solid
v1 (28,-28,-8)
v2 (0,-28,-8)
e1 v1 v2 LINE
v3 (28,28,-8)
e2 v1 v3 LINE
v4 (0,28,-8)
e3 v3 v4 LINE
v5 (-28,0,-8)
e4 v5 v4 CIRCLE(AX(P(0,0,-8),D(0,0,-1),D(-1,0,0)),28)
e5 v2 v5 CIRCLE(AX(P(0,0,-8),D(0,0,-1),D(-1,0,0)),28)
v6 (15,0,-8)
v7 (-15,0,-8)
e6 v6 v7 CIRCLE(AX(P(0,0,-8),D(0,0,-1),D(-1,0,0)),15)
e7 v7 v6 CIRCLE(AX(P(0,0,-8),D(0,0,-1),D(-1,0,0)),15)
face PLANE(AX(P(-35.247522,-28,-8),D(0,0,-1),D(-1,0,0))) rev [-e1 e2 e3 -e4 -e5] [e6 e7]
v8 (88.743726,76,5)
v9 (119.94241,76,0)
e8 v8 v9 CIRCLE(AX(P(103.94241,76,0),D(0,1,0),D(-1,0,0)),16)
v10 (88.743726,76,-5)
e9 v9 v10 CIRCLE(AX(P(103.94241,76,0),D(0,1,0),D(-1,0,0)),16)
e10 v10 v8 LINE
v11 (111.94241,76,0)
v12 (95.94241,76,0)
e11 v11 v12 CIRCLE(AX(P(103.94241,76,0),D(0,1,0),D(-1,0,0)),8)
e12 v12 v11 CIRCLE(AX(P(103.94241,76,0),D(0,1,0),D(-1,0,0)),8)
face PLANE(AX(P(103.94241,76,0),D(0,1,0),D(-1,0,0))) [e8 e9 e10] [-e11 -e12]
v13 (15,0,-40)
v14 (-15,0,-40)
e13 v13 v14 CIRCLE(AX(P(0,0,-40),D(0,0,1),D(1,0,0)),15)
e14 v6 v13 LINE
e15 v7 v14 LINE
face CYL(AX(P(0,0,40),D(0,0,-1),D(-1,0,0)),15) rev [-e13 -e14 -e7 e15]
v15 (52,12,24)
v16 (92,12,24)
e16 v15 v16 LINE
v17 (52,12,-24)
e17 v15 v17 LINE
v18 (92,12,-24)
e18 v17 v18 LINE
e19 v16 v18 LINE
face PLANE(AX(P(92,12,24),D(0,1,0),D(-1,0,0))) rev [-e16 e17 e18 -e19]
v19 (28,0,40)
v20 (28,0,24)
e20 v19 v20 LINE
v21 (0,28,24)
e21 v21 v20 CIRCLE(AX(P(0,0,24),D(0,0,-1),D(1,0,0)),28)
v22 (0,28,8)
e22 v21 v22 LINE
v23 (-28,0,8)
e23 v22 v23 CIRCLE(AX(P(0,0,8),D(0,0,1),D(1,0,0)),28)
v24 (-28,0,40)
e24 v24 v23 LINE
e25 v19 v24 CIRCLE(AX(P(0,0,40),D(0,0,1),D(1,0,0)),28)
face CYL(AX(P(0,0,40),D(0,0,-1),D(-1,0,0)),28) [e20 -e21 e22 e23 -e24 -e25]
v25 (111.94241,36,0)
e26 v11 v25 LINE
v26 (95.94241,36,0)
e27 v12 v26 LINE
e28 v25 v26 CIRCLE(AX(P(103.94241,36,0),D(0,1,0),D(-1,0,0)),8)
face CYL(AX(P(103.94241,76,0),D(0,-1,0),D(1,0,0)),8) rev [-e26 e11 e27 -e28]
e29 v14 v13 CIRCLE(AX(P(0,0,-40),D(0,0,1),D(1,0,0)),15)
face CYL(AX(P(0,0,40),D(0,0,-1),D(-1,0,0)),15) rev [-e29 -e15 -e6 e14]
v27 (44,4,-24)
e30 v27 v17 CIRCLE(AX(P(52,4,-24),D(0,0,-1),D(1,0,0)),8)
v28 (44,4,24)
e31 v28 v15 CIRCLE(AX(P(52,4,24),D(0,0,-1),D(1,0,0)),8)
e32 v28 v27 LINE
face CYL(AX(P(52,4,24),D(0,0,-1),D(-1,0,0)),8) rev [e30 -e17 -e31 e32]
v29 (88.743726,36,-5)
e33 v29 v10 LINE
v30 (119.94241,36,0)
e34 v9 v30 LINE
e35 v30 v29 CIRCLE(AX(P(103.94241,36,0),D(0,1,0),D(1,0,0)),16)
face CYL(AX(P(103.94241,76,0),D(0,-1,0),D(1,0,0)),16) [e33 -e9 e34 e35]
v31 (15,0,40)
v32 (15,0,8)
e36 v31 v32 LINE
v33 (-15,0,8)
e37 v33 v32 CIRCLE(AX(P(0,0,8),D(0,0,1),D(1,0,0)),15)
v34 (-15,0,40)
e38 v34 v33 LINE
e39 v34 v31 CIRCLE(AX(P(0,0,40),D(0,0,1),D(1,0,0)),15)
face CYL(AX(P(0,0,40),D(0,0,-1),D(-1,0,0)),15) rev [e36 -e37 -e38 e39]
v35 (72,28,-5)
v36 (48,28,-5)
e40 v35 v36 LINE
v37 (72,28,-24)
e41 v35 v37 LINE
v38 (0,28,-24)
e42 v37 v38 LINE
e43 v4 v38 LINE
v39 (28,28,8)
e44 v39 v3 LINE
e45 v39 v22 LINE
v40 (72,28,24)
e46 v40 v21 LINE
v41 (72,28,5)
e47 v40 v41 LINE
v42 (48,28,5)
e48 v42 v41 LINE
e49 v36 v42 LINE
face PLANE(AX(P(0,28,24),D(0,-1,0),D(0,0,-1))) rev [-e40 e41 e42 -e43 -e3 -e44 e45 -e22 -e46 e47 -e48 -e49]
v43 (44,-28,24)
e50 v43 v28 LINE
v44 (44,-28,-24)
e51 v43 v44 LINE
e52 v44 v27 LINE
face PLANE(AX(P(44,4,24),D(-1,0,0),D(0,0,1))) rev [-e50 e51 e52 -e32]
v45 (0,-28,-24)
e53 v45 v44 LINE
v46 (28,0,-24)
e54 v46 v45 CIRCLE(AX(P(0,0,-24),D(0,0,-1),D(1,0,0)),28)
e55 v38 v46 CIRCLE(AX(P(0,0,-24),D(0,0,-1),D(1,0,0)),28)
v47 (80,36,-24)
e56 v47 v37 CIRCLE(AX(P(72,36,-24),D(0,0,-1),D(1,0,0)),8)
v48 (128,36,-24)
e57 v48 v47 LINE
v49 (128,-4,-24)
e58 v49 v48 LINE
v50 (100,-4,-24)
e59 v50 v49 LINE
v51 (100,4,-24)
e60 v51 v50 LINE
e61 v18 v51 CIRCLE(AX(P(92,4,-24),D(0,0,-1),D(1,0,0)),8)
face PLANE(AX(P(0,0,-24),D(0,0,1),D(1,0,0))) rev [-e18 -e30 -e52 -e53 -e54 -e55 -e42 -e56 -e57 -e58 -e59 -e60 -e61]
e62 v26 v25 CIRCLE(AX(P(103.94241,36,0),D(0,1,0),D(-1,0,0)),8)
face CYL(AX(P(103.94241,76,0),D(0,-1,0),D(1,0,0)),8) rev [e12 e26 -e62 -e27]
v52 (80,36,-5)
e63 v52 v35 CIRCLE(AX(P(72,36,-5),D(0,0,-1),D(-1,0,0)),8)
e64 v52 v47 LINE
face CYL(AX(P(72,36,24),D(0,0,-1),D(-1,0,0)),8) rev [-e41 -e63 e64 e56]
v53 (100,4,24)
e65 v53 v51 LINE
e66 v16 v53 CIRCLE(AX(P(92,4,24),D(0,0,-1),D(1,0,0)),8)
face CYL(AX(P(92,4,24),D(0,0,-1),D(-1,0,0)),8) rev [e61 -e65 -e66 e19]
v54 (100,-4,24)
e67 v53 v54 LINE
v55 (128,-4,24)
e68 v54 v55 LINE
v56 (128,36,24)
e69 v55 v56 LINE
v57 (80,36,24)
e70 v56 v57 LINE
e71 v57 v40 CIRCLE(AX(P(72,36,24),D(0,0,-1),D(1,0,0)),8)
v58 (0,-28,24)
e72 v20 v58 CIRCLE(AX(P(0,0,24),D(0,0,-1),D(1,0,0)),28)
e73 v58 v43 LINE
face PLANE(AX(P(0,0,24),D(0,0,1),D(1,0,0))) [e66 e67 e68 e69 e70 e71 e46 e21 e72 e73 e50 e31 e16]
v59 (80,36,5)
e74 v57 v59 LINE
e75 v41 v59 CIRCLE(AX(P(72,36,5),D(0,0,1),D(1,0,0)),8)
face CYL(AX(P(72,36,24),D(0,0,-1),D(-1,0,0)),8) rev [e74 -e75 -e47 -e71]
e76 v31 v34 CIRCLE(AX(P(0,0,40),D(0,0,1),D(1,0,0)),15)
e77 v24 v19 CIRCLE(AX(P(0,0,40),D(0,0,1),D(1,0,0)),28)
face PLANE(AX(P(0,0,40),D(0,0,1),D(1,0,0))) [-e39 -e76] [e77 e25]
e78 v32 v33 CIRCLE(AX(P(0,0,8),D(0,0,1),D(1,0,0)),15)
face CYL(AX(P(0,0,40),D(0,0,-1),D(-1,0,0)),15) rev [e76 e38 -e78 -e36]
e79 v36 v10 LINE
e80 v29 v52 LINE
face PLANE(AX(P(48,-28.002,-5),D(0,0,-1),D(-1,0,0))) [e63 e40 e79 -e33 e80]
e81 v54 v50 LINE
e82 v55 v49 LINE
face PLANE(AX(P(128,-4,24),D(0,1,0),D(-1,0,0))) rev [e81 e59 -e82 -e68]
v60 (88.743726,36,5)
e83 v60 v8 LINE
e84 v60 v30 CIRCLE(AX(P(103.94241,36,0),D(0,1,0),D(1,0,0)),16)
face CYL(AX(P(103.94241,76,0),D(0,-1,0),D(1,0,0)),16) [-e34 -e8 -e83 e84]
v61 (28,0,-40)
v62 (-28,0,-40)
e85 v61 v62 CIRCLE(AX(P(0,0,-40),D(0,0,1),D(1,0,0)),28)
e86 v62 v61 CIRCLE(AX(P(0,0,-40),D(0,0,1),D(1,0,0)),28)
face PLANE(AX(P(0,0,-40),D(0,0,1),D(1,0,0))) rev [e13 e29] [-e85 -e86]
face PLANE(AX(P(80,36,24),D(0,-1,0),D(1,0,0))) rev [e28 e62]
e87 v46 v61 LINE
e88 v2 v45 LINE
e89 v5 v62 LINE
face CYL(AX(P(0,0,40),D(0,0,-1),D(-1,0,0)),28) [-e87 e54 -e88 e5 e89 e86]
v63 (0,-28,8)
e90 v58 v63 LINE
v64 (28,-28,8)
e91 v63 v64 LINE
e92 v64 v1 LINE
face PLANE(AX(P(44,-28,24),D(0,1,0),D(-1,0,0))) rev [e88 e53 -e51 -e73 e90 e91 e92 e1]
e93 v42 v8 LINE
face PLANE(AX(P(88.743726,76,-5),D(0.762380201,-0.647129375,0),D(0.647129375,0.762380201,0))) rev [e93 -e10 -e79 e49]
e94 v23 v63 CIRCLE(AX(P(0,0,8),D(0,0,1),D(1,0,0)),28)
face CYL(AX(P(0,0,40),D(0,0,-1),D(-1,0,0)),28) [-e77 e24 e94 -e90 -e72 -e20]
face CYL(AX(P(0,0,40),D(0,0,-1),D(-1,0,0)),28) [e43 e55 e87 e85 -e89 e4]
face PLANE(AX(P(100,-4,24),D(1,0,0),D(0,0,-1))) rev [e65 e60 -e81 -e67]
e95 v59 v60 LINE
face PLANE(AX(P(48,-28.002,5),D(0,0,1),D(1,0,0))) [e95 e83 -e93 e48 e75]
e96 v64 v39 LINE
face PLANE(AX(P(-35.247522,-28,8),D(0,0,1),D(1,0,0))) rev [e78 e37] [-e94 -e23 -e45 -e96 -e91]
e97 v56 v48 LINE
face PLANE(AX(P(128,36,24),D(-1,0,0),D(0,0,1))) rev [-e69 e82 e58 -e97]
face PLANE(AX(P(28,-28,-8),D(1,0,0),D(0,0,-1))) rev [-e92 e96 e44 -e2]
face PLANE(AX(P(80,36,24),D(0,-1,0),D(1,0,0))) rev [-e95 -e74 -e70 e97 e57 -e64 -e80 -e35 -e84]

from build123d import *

# Parameters (mm, degrees)
PIVOT_HUB_SKETCH_R            = 28
PIVOT_HUB_SKETCH_R_2          = 15
PIVOT_HUB_56_BORE_30_DEPTH    = 40
LINK_ARM_DEPTH                = 24
FORK_SLOT_SKETCH_W            = 63.247521784
FORK_SLOT_SKETCH_H            = 16
FORK_SLOT_16_DEPTH            = 146.327216997
UPRIGHT_BOSS_SKETCH_R         = 16
UPRIGHT_BOSS_SKETCH_R_2       = 8
UPRIGHT_BOSS_32_BORE_16_DEPTH = 40
JUNCTION_PAD_REACH            = 171.706
TRIANGULAR_RELIEF_CUT_DEPTH   = 10


with BuildPart() as part:
    # Pivot Hub Sketch → Pivot Hub Ø56 Bore Ø30 (new, symmetric)
    with BuildSketch(Plane.XY):
        Circle(PIVOT_HUB_SKETCH_R)
        Circle(PIVOT_HUB_SKETCH_R_2, mode=Mode.SUBTRACT)
    extrude(amount=PIVOT_HUB_56_BORE_30_DEPTH, both=True)

    # Link Arm Profile → Link Arm (add, symmetric)
    with BuildSketch(Plane.XY):
        with BuildLine():
            Line((0, 28), (72, 28))
            ThreePointArc((72, 28), (77.656854249, 30.343145751), (80, 36))
            Line((80, 36), (128, 36))
            Line((128, 36), (128, -4))
            Line((128, -4), (100, -4))
            Line((100, -4), (100, 4))
            ThreePointArc((100, 4), (97.656854249, 9.656854249), (92, 12))
            Line((92, 12), (52, 12))
            ThreePointArc((52, 12), (46.343145751, 9.656854249), (44, 4))
            Line((44, 4), (44, -28))
            Line((44, -28), (0, -28))
            ThreePointArc((0, -28), (28, 0), (0, 28))
        make_face()
    extrude(amount=LINK_ARM_DEPTH, both=True)

    # Fork Slot Sketch → Fork Slot 16 (cut, through all)
    with BuildSketch(Plane(origin=(0, 28, 0), x_dir=(1, 0, 0), z_dir=(0, 1, 0))):
        with Locations((-3.623760892, 0)):
            Rectangle(FORK_SLOT_SKETCH_W, FORK_SLOT_SKETCH_H)
    extrude(amount=-FORK_SLOT_16_DEPTH, mode=Mode.SUBTRACT)

    # Upright Boss Sketch → Upright Boss Ø32 Bore Ø16 (add)
    with BuildSketch(Plane(origin=(0, 36, 0), x_dir=(1, 0, 0), z_dir=(0, 1, 0))):
        with Locations((103.942410132, 0)):
            Circle(UPRIGHT_BOSS_SKETCH_R)
        with Locations(Location((103.942410132, 0, 0), (0, 0, 180))):
            Circle(UPRIGHT_BOSS_SKETCH_R_2, mode=Mode.SUBTRACT)
    extrude(amount=UPRIGHT_BOSS_32_BORE_16_DEPTH)

    # Junction Pad Sketch → Junction Pad (add, up to next)
    with BuildSketch(Plane(origin=(0, 76, 0), x_dir=(1, 0, 0), z_dir=(0, 1, 0)), mode=Mode.PRIVATE) as junction_pad_sk1:
        with BuildLine():
            Line((48, 5), (88.743725978, 5))
            ThreePointArc((88.743725978, 5), (87.942410132, 0), (88.743725978, -5))
            Line((88.743725978, -5), (48, -5))
            Line((48, -5), (48, 5))
        make_face()
    junction_pad_tool1 = extrude(junction_pad_sk1.sketch, amount=-JUNCTION_PAD_REACH, mode=Mode.PRIVATE) - part.part
    add(junction_pad_tool1.solids().sort_by_distance((68.104095, 76, 0))[0])

    # Relief Cut Sketch → Triangular Relief Cut (cut)
    with BuildSketch(Plane.XY.offset(5)):
        Polygon((88.743725978, 76), (48, 28), (48, 76), align=None)
    extrude(amount=-TRIANGULAR_RELIEF_CUT_DEPTH, mode=Mode.SUBTRACT)


solid = part.part
